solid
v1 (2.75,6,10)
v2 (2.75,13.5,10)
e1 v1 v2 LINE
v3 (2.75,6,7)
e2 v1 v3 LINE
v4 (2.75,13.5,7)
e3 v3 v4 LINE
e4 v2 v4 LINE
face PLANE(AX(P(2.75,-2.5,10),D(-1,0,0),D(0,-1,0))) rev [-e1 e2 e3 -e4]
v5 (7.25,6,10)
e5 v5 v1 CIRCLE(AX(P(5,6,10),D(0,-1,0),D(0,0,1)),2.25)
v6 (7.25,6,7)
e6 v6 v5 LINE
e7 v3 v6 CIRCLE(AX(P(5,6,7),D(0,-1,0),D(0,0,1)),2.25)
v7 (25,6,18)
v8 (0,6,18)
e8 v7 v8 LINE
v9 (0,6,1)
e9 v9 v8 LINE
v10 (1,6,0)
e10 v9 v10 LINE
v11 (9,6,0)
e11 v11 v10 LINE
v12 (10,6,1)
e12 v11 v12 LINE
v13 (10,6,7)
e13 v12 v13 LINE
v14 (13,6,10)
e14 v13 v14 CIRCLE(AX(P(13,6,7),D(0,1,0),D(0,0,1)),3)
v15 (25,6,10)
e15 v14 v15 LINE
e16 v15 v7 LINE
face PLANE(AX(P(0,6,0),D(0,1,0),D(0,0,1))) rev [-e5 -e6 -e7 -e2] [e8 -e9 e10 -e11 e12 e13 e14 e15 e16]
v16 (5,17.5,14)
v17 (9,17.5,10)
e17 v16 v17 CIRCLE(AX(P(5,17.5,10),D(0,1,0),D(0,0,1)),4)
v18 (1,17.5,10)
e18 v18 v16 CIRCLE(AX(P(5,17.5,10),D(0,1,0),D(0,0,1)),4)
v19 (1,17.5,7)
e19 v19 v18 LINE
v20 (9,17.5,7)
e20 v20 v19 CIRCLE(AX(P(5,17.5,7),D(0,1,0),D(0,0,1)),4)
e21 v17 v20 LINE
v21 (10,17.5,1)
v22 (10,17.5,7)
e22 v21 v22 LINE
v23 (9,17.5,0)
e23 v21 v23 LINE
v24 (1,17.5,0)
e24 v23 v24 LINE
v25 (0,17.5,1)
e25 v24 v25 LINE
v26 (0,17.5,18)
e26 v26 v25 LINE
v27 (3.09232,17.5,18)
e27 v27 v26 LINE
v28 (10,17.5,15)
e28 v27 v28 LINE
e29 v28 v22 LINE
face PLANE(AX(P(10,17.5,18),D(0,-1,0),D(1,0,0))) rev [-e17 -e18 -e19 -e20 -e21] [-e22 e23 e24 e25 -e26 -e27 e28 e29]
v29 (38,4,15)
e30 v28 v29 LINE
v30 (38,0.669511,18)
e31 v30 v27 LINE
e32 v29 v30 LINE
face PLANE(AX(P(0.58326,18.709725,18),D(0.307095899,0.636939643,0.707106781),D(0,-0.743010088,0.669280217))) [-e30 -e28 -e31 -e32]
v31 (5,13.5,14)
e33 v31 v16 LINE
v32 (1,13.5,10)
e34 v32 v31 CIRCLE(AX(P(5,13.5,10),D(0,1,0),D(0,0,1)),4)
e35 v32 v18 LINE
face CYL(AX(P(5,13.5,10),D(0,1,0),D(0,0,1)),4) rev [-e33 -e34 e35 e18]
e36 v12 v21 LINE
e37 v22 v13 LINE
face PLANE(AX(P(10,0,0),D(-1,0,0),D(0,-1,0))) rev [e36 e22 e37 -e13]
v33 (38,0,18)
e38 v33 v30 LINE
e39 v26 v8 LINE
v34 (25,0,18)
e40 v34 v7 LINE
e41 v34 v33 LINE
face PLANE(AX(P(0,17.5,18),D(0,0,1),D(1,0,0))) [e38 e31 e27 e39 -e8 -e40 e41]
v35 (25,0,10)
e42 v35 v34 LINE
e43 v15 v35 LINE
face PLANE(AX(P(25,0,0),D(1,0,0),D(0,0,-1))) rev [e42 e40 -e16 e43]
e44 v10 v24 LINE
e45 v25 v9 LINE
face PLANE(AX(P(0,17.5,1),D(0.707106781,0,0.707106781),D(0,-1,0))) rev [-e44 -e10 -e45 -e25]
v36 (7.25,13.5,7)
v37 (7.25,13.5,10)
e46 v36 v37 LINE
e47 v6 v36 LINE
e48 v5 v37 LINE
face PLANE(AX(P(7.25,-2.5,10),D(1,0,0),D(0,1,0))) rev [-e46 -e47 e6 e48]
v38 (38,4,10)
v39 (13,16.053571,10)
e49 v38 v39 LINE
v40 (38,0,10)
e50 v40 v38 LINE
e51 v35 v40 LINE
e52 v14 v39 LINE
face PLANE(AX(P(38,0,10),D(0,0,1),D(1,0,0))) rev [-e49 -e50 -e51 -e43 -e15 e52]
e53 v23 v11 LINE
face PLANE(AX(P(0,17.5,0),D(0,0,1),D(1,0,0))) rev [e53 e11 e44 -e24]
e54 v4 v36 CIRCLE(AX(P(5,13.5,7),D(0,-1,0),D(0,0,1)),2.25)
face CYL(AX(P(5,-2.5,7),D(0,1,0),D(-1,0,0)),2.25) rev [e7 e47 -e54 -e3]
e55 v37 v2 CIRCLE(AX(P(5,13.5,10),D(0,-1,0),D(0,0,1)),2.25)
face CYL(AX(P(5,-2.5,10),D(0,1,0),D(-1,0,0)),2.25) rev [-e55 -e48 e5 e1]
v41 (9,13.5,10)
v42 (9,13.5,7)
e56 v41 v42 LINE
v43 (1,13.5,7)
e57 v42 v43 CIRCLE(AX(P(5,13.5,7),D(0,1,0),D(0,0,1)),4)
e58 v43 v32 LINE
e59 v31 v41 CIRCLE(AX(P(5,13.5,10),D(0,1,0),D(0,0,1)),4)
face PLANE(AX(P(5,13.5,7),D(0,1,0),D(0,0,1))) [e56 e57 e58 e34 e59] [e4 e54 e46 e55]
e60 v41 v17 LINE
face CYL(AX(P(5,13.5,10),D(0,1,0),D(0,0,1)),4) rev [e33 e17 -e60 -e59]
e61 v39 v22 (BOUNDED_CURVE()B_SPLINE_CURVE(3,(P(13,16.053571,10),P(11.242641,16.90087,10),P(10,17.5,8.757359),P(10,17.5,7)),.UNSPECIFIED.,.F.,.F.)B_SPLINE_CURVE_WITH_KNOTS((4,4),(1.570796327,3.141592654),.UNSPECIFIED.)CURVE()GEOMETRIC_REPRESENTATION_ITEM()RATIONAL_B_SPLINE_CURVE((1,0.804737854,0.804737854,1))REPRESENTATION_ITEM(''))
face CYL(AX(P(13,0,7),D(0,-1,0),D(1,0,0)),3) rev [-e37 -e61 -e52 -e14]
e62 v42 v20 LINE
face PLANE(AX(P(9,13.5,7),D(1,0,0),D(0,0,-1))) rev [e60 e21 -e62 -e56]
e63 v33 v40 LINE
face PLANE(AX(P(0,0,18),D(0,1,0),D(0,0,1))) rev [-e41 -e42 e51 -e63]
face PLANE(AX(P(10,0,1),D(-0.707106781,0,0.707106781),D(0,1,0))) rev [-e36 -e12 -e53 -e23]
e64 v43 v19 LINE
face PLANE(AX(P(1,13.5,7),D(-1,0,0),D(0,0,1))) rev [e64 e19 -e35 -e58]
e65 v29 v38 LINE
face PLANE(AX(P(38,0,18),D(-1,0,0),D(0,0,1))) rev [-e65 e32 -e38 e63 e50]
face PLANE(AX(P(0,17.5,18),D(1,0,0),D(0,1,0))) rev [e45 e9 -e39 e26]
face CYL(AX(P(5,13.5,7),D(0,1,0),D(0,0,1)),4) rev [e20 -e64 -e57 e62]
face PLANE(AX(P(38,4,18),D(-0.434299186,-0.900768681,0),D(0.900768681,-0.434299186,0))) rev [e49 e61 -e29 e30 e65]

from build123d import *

# Parameters (mm, degrees)
BOSS_EXTRUDE1_DEPTH = 18
CHAMFER1_SIZE       = 3
CUT_EXTRUDE1_DEPTH  = 20
CUT_EXTRUDE3_DEPTH  = 4
SKETCH3_W           = 25
SKETCH3_H           = 6
CUT_EXTRUDE2_DEPTH  = 46.543934832
SKETCH5_W           = 28
SKETCH5_H           = 10
CUT_EXTRUDE4_DEPTH  = 46.543934832
FILLET1_R           = 3
CHAMFER2_SIZE       = 1


with BuildPart() as part:
    # Sketch1 → Boss-Extrude1 (new body)
    with BuildSketch(Plane.XY):
        Polygon((0, 17.5), (0, 0), (38, 0), (38, 4), (10, 17.5), align=None)
    extrude(amount=BOSS_EXTRUDE1_DEPTH)

    # Chamfer1
    chamfer1_edges = [part.edges().sort_by_distance(p)[0] for p in [
        (24, 10.75, 18),
    ]]
    chamfer(chamfer1_edges, length=CHAMFER1_SIZE)

    # Sketch2 → Cut-Extrude1 (cut)
    with BuildSketch(Plane(origin=(0, 17.5, 0), x_dir=(1, 0, 0), z_dir=(0, 1, 0))):
        with BuildLine():
            Line((2.75, -10), (2.75, -7))
            ThreePointArc((2.75, -7), (5, -4.75), (7.25, -7))
            Line((7.25, -7), (7.25, -10))
            ThreePointArc((7.25, -10), (5, -12.25), (2.75, -10))
        make_face()
    extrude(amount=-CUT_EXTRUDE1_DEPTH, mode=Mode.SUBTRACT)

    # Sketch4 → Cut-Extrude3 (cut)
    with BuildSketch(Plane(origin=(0, 17.5, 0), x_dir=(1, 0, 0), z_dir=(0, 1, 0))):
        with BuildLine():
            Line((9, -7), (9, -10))
            ThreePointArc((9, -10), (5, -14), (1, -10))
            Line((1, -10), (1, -7))
            ThreePointArc((1, -7), (5, -3), (9, -7))
        make_face()
    extrude(amount=-CUT_EXTRUDE3_DEPTH, mode=Mode.SUBTRACT)

    # Sketch3 → Cut-Extrude2 (cut, through all)
    with BuildSketch(Plane.XY.offset(18)):
        with Locations((12.5, 3)):
            Rectangle(SKETCH3_W, SKETCH3_H)
    extrude(amount=-CUT_EXTRUDE2_DEPTH, mode=Mode.SUBTRACT)

    # Sketch5 → Cut-Extrude4 (cut, through all)
    with BuildSketch(Plane(origin=(0, 17.5, 0), x_dir=(-1, 0, 0), z_dir=(0, 1, 0))):
        with Locations((-24, 5)):
            Rectangle(SKETCH5_W, SKETCH5_H)
    extrude(amount=-CUT_EXTRUDE4_DEPTH, mode=Mode.SUBTRACT)

    # Fillet1
    fillet1_edges = [part.edges().sort_by_distance(p)[0] for p in [
        (10, 11.75, 10),
    ]]
    fillet(fillet1_edges, radius=FILLET1_R)

    # Chamfer2
    chamfer2_edges = [part.edges().sort_by_distance(p)[0] for p in [
        (0, 11.75, 0),
        (10, 11.75, 0),
    ]]
    chamfer(chamfer2_edges, length=CHAMFER2_SIZE)


solid = part.part
